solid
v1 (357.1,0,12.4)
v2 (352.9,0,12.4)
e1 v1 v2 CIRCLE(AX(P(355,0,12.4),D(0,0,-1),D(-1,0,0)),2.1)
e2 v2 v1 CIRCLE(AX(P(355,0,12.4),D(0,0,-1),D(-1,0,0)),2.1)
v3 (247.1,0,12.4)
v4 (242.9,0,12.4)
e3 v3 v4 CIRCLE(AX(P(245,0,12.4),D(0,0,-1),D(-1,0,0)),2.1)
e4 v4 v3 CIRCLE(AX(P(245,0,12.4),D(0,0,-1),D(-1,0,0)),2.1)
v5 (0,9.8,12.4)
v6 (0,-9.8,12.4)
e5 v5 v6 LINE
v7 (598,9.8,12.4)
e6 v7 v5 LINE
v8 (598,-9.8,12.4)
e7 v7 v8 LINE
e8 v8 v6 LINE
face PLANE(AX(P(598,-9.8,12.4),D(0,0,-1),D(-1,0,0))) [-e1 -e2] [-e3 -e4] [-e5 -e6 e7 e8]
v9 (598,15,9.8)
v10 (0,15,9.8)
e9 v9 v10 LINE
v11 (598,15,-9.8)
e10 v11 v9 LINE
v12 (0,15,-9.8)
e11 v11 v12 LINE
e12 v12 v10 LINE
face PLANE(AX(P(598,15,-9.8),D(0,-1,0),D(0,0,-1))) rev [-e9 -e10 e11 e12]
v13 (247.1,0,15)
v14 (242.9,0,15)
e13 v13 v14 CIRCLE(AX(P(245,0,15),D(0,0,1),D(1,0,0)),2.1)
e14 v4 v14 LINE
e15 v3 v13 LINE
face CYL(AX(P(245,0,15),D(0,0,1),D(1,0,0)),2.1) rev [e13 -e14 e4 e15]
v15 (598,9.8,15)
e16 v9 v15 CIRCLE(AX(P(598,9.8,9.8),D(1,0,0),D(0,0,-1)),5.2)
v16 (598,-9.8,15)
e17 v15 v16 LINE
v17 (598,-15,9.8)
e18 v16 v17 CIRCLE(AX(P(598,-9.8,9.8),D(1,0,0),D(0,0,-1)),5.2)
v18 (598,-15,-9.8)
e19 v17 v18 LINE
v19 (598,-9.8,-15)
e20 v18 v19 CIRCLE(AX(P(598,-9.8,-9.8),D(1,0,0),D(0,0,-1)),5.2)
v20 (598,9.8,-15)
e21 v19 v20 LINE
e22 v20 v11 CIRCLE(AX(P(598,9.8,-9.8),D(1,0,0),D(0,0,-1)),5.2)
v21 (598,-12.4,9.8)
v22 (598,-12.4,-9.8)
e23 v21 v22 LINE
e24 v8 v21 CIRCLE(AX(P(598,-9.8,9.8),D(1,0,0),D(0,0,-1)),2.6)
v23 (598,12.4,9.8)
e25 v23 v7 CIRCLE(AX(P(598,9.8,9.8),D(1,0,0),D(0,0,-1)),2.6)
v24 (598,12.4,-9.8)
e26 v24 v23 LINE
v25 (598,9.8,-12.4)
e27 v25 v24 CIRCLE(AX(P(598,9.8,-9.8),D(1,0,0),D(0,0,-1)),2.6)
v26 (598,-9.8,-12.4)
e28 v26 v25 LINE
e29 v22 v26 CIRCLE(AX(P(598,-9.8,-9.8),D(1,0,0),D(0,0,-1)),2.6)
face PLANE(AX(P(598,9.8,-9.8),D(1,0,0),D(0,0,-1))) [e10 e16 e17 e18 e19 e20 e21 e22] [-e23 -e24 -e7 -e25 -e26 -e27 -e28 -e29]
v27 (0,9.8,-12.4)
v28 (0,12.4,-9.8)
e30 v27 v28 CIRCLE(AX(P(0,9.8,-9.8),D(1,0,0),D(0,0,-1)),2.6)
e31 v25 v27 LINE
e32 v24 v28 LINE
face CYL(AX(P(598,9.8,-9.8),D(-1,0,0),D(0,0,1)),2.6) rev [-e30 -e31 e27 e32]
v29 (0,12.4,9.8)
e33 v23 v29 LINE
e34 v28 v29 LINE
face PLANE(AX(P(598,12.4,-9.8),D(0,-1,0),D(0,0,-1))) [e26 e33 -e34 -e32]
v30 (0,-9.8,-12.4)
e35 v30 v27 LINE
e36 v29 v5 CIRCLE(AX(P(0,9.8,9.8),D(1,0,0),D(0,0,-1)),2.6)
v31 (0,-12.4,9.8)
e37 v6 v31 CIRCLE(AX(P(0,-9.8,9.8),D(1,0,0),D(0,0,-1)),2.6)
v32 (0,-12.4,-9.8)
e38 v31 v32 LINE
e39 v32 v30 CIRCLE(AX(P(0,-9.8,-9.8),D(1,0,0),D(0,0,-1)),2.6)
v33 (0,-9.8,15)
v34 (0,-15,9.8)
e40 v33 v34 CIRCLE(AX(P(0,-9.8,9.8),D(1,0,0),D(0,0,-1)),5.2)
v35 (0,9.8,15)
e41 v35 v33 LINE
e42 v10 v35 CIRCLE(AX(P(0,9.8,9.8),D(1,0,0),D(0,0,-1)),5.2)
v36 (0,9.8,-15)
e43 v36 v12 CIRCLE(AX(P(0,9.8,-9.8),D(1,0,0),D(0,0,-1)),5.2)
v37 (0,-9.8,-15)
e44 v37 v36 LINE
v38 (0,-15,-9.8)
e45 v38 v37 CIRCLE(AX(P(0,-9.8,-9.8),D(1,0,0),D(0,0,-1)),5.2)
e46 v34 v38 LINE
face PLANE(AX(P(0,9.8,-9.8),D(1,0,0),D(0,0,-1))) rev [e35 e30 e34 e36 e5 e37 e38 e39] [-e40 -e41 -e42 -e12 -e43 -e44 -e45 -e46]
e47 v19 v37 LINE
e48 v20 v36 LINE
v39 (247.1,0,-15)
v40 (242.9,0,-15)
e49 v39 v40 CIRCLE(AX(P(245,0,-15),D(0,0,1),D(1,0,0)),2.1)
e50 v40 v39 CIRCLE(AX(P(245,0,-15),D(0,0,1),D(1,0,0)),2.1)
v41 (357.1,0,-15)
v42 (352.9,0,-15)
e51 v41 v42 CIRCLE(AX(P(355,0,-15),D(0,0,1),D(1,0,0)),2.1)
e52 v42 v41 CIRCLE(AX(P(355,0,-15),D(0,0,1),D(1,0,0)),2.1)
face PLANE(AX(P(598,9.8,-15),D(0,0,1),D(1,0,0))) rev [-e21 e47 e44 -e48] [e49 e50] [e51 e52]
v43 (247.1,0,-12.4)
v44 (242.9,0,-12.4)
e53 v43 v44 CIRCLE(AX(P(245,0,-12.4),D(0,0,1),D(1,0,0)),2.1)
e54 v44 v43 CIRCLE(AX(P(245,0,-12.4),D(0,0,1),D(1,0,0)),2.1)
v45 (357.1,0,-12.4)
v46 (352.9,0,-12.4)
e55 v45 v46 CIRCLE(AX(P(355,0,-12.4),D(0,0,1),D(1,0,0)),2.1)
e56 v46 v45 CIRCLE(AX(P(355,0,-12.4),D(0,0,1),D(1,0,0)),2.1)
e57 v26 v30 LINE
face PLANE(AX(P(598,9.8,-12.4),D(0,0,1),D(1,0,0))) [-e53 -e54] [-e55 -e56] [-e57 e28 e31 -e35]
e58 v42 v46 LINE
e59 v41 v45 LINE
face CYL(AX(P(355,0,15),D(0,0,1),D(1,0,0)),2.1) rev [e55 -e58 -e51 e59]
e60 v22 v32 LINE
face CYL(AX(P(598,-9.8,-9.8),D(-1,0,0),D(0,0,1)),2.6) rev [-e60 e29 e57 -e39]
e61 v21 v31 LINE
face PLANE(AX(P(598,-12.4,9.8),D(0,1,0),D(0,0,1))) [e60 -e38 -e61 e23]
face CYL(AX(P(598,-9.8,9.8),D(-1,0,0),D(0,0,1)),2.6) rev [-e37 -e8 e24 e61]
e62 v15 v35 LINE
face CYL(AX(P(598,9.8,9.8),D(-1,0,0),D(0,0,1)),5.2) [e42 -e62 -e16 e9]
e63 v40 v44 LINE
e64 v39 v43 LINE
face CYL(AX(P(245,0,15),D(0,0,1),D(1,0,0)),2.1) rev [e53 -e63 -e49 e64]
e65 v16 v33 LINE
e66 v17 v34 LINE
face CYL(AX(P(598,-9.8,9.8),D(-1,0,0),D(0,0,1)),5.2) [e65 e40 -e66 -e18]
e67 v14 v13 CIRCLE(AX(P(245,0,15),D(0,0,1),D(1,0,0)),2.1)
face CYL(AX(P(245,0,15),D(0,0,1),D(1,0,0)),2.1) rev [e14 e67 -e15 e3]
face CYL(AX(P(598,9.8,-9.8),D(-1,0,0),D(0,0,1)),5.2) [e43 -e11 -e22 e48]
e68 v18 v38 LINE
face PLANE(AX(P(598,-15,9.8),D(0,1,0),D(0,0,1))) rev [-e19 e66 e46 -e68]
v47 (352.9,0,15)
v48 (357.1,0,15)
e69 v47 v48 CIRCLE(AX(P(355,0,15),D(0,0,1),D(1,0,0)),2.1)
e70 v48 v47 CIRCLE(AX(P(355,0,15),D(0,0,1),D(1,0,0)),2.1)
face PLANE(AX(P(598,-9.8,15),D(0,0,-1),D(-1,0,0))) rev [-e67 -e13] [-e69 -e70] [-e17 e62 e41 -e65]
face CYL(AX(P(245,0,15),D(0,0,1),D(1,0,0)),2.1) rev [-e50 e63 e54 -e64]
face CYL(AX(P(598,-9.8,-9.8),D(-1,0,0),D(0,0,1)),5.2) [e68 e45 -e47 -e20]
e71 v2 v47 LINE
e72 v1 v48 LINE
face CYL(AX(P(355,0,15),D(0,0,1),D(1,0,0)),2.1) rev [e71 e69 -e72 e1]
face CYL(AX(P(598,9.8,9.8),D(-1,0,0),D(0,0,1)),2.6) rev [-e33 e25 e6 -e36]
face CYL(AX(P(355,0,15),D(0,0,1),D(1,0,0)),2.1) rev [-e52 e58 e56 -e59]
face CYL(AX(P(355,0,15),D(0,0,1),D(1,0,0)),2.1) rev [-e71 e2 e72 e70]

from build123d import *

# Parameters (mm, degrees)
MEMBER_1_DEPTH     = 598
HOLE_WIZARD_M5_1_D = 4.2


with BuildPart() as part:
    # Sketch1 → Member 1 (new body)
    with BuildSketch(Plane(origin=(0, 0, 0), x_dir=(0, 0, -1), z_dir=(1, 0, 0))):
        with BuildLine():
            Line((-9.8, -15), (9.8, -15))
            ThreePointArc((9.8, -15), (13.476955262, -13.476955262), (15, -9.8))
            Line((15, -9.8), (15, 9.8))
            ThreePointArc((15, 9.8), (13.476955262, 13.476955262), (9.8, 15))
            Line((9.8, 15), (-9.8, 15))
            ThreePointArc((-9.8, 15), (-13.476955262, 13.476955262), (-15, 9.8))
            Line((-15, 9.8), (-15, -9.8))
            ThreePointArc((-15, -9.8), (-13.476955262, -13.476955262), (-9.8, -15))
        make_face()
        with BuildLine():
            Line((-9.8, -12.4), (9.8, -12.4))
            ThreePointArc((9.8, -12.4), (11.638477631, -11.638477631), (12.4, -9.8))
            Line((12.4, -9.8), (12.4, 9.8))
            ThreePointArc((12.4, 9.8), (11.638477631, 11.638477631), (9.8, 12.4))
            Line((9.8, 12.4), (-9.8, 12.4))
            ThreePointArc((-9.8, 12.4), (-11.638477631, 11.638477631), (-12.4, 9.8))
            Line((-12.4, 9.8), (-12.4, -9.8))
            ThreePointArc((-12.4, -9.8), (-11.638477631, -11.638477631), (-9.8, -12.4))
        make_face(mode=Mode.SUBTRACT)
    extrude(amount=MEMBER_1_DEPTH)

    # M5 螺纹孔1 (through all)
    with Locations(Plane.XY.offset(15)):
        with Locations((355.000000009, 0), (245.000000009, 0)):
            Hole(HOLE_WIZARD_M5_1_D / 2)


solid = part.part
